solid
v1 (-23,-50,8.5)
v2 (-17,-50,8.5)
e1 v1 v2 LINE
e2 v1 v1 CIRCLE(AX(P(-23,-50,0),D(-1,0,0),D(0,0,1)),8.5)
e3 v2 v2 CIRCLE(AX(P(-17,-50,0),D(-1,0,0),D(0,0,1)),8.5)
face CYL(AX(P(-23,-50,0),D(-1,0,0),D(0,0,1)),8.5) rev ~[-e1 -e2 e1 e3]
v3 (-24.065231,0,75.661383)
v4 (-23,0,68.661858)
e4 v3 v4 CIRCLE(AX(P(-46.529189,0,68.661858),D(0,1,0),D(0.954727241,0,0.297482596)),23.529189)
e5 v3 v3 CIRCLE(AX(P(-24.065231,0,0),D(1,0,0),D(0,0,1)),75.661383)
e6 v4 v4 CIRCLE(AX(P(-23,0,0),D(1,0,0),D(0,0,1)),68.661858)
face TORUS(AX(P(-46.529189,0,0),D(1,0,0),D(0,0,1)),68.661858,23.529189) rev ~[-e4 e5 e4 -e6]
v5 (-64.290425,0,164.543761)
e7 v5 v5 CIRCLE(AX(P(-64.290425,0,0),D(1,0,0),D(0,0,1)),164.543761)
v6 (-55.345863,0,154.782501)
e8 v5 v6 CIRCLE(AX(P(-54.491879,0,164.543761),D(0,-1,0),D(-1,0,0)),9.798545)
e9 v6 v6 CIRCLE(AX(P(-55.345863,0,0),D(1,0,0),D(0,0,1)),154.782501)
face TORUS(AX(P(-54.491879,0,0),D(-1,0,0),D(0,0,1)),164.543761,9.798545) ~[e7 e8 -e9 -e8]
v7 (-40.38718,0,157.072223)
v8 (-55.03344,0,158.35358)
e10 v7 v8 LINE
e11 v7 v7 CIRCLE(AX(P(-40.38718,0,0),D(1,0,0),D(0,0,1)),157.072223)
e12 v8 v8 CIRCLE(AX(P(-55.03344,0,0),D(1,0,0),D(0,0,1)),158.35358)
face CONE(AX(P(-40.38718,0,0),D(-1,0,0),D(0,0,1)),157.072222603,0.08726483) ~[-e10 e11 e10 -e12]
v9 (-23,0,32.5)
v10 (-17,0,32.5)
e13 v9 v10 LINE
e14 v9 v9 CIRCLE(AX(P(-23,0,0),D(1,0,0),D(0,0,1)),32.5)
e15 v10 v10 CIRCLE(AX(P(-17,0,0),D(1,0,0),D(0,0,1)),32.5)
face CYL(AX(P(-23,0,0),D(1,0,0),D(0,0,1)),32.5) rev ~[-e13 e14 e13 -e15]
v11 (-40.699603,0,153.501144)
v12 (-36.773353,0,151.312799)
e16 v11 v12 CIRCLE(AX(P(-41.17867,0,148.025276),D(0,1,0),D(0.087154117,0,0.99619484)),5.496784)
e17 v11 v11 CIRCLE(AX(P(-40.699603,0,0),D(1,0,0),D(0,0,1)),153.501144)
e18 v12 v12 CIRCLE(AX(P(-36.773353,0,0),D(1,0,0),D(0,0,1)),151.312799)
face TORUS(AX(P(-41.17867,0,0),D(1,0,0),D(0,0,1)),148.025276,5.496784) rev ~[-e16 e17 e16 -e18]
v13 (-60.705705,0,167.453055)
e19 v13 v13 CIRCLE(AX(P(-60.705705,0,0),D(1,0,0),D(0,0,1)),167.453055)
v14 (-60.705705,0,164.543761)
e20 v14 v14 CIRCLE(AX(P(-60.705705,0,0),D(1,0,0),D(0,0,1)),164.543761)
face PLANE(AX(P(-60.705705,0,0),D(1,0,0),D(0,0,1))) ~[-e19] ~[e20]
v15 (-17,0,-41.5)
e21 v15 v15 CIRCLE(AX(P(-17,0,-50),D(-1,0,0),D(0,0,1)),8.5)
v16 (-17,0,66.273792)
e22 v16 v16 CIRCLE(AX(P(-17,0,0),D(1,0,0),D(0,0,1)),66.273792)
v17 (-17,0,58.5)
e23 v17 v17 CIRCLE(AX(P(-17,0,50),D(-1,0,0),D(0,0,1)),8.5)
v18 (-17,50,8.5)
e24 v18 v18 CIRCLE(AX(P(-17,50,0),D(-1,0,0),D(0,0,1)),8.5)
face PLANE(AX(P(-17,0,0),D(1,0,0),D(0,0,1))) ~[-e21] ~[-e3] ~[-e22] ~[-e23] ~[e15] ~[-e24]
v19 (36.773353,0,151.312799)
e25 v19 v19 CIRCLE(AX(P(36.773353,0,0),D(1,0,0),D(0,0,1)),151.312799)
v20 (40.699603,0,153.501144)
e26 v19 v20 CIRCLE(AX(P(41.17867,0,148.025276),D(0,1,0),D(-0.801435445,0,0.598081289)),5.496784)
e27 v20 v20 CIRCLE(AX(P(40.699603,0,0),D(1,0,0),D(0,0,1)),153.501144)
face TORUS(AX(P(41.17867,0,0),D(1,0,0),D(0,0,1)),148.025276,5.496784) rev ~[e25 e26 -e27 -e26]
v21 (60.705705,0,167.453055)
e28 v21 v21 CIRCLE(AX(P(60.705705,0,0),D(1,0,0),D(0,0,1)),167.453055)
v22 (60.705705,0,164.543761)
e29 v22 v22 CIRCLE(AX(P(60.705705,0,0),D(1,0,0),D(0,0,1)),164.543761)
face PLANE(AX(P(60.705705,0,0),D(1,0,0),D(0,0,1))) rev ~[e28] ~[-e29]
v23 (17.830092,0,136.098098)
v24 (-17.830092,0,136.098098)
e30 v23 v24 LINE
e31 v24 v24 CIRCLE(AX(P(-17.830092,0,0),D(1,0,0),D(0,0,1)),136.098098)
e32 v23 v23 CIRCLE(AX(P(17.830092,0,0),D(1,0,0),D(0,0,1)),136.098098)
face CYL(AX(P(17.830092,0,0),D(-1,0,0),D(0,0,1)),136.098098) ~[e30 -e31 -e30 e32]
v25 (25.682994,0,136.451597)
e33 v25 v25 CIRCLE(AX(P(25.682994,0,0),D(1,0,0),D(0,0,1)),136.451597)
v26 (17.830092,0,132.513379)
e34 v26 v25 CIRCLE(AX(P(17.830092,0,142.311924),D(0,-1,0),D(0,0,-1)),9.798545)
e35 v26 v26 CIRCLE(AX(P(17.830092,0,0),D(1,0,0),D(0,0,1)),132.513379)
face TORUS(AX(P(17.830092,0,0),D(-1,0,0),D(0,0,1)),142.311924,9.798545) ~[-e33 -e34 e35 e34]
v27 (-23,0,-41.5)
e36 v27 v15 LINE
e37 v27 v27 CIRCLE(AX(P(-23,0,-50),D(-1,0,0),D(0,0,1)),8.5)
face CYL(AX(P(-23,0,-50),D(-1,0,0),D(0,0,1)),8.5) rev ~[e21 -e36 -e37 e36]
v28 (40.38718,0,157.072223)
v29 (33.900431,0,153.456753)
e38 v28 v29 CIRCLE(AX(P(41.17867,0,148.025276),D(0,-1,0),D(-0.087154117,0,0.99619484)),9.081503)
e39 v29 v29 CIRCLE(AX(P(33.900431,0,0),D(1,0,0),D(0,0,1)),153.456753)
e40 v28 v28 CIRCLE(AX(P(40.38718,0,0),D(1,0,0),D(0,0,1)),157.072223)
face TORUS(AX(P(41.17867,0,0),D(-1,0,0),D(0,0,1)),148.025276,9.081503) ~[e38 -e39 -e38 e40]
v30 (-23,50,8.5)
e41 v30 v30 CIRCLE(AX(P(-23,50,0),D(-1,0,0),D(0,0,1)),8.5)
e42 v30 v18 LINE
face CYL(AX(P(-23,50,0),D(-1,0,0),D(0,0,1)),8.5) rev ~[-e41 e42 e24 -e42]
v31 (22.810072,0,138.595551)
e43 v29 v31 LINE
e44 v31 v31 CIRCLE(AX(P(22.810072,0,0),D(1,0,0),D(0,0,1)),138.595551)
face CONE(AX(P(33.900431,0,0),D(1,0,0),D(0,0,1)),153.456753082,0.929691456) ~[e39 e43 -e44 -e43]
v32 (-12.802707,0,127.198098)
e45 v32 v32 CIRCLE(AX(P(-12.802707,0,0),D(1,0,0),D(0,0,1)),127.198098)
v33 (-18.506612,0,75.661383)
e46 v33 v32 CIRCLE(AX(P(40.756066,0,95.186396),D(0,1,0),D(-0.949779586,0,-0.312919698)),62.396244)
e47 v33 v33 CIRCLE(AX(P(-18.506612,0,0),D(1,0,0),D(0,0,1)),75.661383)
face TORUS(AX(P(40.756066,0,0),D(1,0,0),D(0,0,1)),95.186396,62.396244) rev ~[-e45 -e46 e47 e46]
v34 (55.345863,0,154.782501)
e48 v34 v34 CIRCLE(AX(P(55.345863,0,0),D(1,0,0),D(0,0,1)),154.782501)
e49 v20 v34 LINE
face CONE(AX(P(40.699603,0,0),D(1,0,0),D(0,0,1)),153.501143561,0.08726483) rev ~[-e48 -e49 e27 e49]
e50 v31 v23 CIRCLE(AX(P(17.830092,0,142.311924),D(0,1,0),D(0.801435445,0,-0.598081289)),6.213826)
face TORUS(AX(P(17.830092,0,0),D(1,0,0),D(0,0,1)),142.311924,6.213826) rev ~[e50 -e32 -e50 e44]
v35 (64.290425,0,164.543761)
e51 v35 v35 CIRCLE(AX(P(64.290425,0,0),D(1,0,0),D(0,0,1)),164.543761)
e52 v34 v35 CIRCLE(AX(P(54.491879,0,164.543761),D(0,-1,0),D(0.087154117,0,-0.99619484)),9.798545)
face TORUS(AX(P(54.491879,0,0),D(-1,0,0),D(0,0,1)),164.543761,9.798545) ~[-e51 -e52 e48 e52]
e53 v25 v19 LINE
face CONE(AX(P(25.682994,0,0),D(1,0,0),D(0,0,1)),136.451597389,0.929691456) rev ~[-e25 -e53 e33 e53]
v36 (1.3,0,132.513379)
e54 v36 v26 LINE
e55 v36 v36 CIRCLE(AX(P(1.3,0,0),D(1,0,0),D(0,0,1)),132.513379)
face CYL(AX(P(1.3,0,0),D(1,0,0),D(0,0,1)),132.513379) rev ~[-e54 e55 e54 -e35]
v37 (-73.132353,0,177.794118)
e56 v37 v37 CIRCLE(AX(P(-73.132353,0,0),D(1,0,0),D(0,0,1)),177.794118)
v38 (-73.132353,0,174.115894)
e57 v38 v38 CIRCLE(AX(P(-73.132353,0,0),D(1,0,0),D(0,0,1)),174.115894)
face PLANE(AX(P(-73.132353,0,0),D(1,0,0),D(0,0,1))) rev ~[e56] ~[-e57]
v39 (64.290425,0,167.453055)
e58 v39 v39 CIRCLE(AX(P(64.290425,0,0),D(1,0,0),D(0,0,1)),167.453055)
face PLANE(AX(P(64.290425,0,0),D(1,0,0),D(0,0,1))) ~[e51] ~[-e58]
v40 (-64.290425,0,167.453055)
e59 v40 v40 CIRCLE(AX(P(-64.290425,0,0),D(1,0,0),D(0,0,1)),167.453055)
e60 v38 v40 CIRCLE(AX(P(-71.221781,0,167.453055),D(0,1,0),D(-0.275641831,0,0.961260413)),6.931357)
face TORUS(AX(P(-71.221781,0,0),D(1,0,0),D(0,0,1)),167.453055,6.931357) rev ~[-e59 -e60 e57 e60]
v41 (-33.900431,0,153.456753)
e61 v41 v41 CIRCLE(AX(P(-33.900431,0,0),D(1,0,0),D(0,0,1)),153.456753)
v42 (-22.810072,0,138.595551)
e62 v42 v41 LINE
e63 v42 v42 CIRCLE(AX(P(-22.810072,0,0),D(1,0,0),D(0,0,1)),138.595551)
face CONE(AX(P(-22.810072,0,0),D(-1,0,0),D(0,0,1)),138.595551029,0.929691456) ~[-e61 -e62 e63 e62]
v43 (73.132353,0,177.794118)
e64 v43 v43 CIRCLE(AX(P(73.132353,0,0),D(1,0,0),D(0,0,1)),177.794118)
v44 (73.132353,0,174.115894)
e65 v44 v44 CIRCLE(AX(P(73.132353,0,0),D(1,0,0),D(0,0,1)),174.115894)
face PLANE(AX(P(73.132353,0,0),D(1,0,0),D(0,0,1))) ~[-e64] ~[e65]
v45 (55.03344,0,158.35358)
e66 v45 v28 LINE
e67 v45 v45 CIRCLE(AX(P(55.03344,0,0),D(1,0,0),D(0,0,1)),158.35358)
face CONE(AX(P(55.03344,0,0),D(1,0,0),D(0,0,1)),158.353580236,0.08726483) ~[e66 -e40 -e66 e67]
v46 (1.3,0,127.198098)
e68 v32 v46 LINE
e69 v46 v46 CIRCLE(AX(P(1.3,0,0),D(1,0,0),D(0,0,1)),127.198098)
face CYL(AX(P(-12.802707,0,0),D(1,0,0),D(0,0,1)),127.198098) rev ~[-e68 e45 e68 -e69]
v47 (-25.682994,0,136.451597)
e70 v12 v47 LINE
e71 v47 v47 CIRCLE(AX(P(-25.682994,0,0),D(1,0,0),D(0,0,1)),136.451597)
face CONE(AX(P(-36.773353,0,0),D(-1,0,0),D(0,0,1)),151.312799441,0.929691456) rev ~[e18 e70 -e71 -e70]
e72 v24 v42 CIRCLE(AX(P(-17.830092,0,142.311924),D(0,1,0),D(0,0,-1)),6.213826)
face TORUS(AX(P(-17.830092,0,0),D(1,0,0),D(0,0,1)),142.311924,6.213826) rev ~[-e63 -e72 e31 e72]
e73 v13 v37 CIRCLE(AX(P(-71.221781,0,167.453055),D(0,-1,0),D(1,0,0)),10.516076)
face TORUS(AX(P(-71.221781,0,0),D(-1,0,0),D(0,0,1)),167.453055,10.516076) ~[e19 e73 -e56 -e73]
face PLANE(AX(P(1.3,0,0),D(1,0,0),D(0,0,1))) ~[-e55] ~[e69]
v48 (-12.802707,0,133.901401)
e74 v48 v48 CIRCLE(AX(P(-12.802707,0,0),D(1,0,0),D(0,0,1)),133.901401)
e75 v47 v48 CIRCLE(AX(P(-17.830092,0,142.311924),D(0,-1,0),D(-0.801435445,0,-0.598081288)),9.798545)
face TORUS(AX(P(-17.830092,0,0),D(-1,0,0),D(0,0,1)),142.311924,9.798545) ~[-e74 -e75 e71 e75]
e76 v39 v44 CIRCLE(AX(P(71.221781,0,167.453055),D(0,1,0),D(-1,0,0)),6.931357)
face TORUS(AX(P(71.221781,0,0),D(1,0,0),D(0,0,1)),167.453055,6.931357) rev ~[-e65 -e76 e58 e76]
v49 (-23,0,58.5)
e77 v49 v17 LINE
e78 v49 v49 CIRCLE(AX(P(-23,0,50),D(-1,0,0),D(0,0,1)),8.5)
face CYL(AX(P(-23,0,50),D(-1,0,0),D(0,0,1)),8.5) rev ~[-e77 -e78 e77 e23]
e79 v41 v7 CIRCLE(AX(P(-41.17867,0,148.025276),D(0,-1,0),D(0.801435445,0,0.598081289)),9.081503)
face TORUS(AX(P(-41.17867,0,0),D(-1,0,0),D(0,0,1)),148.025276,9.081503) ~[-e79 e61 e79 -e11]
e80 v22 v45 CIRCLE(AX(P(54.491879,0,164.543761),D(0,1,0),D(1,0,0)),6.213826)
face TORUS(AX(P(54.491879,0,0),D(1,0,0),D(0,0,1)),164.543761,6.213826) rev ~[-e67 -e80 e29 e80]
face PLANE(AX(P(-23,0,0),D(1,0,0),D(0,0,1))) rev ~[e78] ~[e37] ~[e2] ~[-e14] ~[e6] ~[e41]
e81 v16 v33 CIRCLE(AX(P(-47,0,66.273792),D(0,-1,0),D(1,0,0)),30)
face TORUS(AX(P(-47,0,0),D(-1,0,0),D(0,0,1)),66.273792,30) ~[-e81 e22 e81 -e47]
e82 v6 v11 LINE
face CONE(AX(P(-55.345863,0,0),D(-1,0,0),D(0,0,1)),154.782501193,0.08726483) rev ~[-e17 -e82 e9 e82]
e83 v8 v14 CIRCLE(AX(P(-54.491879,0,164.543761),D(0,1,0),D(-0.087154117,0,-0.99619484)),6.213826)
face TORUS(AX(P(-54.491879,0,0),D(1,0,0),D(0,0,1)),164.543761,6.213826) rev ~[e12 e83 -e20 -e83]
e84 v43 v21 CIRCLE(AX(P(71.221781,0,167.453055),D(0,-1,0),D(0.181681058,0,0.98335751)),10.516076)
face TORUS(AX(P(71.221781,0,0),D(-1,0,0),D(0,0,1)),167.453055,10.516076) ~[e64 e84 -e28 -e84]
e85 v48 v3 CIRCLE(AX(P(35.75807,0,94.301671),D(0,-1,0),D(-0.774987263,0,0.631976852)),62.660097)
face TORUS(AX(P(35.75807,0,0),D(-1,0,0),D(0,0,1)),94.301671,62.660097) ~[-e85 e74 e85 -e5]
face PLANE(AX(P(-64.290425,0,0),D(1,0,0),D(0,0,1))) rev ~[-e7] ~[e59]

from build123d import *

# Parameters (mm, degrees)
SKETCH_3_R          = 8.5
CUT_EXTRUDE_1_DEPTH = 270.420587168


with BuildPart() as part:
    # 草图2 → 旋转1 (revolve)
    with BuildSketch(Plane.XY, mode=Mode.PRIVATE) as revolve_1_sk:
        with BuildLine():
            Line((55.03343969, 158.353580236), (40.387179575, 157.072222603))
            ThreePointArc((40.387179575, 157.072222603), (36.757353818, 155.957845796), (33.90043136, 153.456753082))
            Line((33.90043136, 153.456753082), (22.81007227, 138.595551029))
            ThreePointArc((22.81007227, 138.595551029), (20.615656314, 136.757442651), (17.830091986, 136.098098151))
            Line((17.830091986, 136.098098151), (-17.830091986, 136.098098151))
            ThreePointArc((-17.830091986, 136.098098151), (-20.615656314, 136.757442651), (-22.81007227, 138.595551029))
            Line((-22.81007227, 138.595551029), (-33.90043136, 153.456753082))
            ThreePointArc((-33.90043136, 153.456753082), (-36.757353818, 155.957845796), (-40.387179575, 157.072222603))
            Line((-40.387179575, 157.072222603), (-55.03343969, 158.353580236))
            ThreePointArc((-55.03343969, 158.353580236), (-59.073188734, 160.345757851), (-60.705705036, 164.543761485))
            Line((-60.705705036, 164.543761485), (-60.705705036, 167.453055254))
            ThreePointArc((-60.705705036, 167.453055254), (-64.495112644, 175.536358254), (-73.132352941, 177.794117647))
            Line((-73.132352941, 177.794117647), (-73.132352941, 174.115893968))
            ThreePointArc((-73.132352941, 174.115893968), (-67.050399463, 172.988692483), (-64.290424508, 167.453055254))
            Line((-64.290424508, 167.453055254), (-64.290424508, 164.543761485))
            ThreePointArc((-64.290424508, 164.543761485), (-61.716119183, 157.923954321), (-55.345862749, 154.782501193))
            Line((-55.345862749, 154.782501193), (-40.699602634, 153.501143561))
            ThreePointArc((-40.699602634, 153.501143561), (-38.50256908, 152.826641973), (-36.773352605, 151.312799441))
            Line((-36.773352605, 151.312799441), (-25.682993515, 136.451597389))
            ThreePointArc((-25.682993515, 136.451597389), (-19.733184391, 132.699966358), (-12.802706935, 133.901401426))
            ThreePointArc((-12.802706935, 133.901401426), (-25.762268543, 106.198547314), (-24.065231305, 75.661382618))
            ThreePointArc((-24.065231305, 75.661382618), (-23.26783219, 72.20191689), (-23, 68.661858362))
            Line((-23, 68.661858362), (-23, 32.5))
            Line((-23, 32.5), (-17, 32.5))
            Line((-17, 32.5), (-17, 66.273791669))
            ThreePointArc((-17, 66.273791669), (-17.379047723, 71.027651805), (-18.506612413, 75.661382618))
            ThreePointArc((-18.506612413, 75.661382618), (-21.261497911, 102.050285854), (-12.802706935, 127.198098151))
            Line((-12.802706935, 127.198098151), (1.3, 127.198098151))
            Line((1.3, 127.198098151), (1.3, 132.513378678))
            Line((1.3, 132.513378678), (17.830091986, 132.513378678))
            ThreePointArc((17.830091986, 132.513378678), (22.222631941, 133.553095131), (25.682993515, 136.451597389))
            Line((25.682993515, 136.451597389), (36.773352605, 151.312799441))
            ThreePointArc((36.773352605, 151.312799441), (38.50256908, 152.826641973), (40.699602634, 153.501143561))
            Line((40.699602634, 153.501143561), (55.345862749, 154.782501193))
            ThreePointArc((55.345862749, 154.782501193), (61.716119183, 157.923954321), (64.290424508, 164.543761485))
            Line((64.290424508, 164.543761485), (64.290424508, 167.453055254))
            ThreePointArc((64.290424508, 167.453055254), (67.050399463, 172.988692483), (73.132352941, 174.115893968))
            Line((73.132352941, 174.115893968), (73.132352941, 177.794117647))
            ThreePointArc((73.132352941, 177.794117647), (64.495112644, 175.536358254), (60.705705036, 167.453055254))
            Line((60.705705036, 167.453055254), (60.705705036, 164.543761485))
            ThreePointArc((60.705705036, 164.543761485), (59.073188734, 160.345757851), (55.03343969, 158.353580236))
        make_face()
    revolve(revolve_1_sk.sketch.rotate(Axis((0, 0, 0), (1, 0, 0)), 90), axis=Axis((0, 0, 0), (1, 0, 0)))

    # 草图3 → 切除-拉伸1 (cut, through all)
    with BuildSketch(Plane.ZY.offset(23)):
        with Locations((0, 50)):
            Circle(SKETCH_3_R)
        with Locations((50, 0)):
            Circle(SKETCH_3_R)
        with Locations((0, -50)):
            Circle(SKETCH_3_R)
        with Locations((-50, 0)):
            Circle(SKETCH_3_R)
    extrude(amount=-CUT_EXTRUDE_1_DEPTH, mode=Mode.SUBTRACT)


solid = part.part
